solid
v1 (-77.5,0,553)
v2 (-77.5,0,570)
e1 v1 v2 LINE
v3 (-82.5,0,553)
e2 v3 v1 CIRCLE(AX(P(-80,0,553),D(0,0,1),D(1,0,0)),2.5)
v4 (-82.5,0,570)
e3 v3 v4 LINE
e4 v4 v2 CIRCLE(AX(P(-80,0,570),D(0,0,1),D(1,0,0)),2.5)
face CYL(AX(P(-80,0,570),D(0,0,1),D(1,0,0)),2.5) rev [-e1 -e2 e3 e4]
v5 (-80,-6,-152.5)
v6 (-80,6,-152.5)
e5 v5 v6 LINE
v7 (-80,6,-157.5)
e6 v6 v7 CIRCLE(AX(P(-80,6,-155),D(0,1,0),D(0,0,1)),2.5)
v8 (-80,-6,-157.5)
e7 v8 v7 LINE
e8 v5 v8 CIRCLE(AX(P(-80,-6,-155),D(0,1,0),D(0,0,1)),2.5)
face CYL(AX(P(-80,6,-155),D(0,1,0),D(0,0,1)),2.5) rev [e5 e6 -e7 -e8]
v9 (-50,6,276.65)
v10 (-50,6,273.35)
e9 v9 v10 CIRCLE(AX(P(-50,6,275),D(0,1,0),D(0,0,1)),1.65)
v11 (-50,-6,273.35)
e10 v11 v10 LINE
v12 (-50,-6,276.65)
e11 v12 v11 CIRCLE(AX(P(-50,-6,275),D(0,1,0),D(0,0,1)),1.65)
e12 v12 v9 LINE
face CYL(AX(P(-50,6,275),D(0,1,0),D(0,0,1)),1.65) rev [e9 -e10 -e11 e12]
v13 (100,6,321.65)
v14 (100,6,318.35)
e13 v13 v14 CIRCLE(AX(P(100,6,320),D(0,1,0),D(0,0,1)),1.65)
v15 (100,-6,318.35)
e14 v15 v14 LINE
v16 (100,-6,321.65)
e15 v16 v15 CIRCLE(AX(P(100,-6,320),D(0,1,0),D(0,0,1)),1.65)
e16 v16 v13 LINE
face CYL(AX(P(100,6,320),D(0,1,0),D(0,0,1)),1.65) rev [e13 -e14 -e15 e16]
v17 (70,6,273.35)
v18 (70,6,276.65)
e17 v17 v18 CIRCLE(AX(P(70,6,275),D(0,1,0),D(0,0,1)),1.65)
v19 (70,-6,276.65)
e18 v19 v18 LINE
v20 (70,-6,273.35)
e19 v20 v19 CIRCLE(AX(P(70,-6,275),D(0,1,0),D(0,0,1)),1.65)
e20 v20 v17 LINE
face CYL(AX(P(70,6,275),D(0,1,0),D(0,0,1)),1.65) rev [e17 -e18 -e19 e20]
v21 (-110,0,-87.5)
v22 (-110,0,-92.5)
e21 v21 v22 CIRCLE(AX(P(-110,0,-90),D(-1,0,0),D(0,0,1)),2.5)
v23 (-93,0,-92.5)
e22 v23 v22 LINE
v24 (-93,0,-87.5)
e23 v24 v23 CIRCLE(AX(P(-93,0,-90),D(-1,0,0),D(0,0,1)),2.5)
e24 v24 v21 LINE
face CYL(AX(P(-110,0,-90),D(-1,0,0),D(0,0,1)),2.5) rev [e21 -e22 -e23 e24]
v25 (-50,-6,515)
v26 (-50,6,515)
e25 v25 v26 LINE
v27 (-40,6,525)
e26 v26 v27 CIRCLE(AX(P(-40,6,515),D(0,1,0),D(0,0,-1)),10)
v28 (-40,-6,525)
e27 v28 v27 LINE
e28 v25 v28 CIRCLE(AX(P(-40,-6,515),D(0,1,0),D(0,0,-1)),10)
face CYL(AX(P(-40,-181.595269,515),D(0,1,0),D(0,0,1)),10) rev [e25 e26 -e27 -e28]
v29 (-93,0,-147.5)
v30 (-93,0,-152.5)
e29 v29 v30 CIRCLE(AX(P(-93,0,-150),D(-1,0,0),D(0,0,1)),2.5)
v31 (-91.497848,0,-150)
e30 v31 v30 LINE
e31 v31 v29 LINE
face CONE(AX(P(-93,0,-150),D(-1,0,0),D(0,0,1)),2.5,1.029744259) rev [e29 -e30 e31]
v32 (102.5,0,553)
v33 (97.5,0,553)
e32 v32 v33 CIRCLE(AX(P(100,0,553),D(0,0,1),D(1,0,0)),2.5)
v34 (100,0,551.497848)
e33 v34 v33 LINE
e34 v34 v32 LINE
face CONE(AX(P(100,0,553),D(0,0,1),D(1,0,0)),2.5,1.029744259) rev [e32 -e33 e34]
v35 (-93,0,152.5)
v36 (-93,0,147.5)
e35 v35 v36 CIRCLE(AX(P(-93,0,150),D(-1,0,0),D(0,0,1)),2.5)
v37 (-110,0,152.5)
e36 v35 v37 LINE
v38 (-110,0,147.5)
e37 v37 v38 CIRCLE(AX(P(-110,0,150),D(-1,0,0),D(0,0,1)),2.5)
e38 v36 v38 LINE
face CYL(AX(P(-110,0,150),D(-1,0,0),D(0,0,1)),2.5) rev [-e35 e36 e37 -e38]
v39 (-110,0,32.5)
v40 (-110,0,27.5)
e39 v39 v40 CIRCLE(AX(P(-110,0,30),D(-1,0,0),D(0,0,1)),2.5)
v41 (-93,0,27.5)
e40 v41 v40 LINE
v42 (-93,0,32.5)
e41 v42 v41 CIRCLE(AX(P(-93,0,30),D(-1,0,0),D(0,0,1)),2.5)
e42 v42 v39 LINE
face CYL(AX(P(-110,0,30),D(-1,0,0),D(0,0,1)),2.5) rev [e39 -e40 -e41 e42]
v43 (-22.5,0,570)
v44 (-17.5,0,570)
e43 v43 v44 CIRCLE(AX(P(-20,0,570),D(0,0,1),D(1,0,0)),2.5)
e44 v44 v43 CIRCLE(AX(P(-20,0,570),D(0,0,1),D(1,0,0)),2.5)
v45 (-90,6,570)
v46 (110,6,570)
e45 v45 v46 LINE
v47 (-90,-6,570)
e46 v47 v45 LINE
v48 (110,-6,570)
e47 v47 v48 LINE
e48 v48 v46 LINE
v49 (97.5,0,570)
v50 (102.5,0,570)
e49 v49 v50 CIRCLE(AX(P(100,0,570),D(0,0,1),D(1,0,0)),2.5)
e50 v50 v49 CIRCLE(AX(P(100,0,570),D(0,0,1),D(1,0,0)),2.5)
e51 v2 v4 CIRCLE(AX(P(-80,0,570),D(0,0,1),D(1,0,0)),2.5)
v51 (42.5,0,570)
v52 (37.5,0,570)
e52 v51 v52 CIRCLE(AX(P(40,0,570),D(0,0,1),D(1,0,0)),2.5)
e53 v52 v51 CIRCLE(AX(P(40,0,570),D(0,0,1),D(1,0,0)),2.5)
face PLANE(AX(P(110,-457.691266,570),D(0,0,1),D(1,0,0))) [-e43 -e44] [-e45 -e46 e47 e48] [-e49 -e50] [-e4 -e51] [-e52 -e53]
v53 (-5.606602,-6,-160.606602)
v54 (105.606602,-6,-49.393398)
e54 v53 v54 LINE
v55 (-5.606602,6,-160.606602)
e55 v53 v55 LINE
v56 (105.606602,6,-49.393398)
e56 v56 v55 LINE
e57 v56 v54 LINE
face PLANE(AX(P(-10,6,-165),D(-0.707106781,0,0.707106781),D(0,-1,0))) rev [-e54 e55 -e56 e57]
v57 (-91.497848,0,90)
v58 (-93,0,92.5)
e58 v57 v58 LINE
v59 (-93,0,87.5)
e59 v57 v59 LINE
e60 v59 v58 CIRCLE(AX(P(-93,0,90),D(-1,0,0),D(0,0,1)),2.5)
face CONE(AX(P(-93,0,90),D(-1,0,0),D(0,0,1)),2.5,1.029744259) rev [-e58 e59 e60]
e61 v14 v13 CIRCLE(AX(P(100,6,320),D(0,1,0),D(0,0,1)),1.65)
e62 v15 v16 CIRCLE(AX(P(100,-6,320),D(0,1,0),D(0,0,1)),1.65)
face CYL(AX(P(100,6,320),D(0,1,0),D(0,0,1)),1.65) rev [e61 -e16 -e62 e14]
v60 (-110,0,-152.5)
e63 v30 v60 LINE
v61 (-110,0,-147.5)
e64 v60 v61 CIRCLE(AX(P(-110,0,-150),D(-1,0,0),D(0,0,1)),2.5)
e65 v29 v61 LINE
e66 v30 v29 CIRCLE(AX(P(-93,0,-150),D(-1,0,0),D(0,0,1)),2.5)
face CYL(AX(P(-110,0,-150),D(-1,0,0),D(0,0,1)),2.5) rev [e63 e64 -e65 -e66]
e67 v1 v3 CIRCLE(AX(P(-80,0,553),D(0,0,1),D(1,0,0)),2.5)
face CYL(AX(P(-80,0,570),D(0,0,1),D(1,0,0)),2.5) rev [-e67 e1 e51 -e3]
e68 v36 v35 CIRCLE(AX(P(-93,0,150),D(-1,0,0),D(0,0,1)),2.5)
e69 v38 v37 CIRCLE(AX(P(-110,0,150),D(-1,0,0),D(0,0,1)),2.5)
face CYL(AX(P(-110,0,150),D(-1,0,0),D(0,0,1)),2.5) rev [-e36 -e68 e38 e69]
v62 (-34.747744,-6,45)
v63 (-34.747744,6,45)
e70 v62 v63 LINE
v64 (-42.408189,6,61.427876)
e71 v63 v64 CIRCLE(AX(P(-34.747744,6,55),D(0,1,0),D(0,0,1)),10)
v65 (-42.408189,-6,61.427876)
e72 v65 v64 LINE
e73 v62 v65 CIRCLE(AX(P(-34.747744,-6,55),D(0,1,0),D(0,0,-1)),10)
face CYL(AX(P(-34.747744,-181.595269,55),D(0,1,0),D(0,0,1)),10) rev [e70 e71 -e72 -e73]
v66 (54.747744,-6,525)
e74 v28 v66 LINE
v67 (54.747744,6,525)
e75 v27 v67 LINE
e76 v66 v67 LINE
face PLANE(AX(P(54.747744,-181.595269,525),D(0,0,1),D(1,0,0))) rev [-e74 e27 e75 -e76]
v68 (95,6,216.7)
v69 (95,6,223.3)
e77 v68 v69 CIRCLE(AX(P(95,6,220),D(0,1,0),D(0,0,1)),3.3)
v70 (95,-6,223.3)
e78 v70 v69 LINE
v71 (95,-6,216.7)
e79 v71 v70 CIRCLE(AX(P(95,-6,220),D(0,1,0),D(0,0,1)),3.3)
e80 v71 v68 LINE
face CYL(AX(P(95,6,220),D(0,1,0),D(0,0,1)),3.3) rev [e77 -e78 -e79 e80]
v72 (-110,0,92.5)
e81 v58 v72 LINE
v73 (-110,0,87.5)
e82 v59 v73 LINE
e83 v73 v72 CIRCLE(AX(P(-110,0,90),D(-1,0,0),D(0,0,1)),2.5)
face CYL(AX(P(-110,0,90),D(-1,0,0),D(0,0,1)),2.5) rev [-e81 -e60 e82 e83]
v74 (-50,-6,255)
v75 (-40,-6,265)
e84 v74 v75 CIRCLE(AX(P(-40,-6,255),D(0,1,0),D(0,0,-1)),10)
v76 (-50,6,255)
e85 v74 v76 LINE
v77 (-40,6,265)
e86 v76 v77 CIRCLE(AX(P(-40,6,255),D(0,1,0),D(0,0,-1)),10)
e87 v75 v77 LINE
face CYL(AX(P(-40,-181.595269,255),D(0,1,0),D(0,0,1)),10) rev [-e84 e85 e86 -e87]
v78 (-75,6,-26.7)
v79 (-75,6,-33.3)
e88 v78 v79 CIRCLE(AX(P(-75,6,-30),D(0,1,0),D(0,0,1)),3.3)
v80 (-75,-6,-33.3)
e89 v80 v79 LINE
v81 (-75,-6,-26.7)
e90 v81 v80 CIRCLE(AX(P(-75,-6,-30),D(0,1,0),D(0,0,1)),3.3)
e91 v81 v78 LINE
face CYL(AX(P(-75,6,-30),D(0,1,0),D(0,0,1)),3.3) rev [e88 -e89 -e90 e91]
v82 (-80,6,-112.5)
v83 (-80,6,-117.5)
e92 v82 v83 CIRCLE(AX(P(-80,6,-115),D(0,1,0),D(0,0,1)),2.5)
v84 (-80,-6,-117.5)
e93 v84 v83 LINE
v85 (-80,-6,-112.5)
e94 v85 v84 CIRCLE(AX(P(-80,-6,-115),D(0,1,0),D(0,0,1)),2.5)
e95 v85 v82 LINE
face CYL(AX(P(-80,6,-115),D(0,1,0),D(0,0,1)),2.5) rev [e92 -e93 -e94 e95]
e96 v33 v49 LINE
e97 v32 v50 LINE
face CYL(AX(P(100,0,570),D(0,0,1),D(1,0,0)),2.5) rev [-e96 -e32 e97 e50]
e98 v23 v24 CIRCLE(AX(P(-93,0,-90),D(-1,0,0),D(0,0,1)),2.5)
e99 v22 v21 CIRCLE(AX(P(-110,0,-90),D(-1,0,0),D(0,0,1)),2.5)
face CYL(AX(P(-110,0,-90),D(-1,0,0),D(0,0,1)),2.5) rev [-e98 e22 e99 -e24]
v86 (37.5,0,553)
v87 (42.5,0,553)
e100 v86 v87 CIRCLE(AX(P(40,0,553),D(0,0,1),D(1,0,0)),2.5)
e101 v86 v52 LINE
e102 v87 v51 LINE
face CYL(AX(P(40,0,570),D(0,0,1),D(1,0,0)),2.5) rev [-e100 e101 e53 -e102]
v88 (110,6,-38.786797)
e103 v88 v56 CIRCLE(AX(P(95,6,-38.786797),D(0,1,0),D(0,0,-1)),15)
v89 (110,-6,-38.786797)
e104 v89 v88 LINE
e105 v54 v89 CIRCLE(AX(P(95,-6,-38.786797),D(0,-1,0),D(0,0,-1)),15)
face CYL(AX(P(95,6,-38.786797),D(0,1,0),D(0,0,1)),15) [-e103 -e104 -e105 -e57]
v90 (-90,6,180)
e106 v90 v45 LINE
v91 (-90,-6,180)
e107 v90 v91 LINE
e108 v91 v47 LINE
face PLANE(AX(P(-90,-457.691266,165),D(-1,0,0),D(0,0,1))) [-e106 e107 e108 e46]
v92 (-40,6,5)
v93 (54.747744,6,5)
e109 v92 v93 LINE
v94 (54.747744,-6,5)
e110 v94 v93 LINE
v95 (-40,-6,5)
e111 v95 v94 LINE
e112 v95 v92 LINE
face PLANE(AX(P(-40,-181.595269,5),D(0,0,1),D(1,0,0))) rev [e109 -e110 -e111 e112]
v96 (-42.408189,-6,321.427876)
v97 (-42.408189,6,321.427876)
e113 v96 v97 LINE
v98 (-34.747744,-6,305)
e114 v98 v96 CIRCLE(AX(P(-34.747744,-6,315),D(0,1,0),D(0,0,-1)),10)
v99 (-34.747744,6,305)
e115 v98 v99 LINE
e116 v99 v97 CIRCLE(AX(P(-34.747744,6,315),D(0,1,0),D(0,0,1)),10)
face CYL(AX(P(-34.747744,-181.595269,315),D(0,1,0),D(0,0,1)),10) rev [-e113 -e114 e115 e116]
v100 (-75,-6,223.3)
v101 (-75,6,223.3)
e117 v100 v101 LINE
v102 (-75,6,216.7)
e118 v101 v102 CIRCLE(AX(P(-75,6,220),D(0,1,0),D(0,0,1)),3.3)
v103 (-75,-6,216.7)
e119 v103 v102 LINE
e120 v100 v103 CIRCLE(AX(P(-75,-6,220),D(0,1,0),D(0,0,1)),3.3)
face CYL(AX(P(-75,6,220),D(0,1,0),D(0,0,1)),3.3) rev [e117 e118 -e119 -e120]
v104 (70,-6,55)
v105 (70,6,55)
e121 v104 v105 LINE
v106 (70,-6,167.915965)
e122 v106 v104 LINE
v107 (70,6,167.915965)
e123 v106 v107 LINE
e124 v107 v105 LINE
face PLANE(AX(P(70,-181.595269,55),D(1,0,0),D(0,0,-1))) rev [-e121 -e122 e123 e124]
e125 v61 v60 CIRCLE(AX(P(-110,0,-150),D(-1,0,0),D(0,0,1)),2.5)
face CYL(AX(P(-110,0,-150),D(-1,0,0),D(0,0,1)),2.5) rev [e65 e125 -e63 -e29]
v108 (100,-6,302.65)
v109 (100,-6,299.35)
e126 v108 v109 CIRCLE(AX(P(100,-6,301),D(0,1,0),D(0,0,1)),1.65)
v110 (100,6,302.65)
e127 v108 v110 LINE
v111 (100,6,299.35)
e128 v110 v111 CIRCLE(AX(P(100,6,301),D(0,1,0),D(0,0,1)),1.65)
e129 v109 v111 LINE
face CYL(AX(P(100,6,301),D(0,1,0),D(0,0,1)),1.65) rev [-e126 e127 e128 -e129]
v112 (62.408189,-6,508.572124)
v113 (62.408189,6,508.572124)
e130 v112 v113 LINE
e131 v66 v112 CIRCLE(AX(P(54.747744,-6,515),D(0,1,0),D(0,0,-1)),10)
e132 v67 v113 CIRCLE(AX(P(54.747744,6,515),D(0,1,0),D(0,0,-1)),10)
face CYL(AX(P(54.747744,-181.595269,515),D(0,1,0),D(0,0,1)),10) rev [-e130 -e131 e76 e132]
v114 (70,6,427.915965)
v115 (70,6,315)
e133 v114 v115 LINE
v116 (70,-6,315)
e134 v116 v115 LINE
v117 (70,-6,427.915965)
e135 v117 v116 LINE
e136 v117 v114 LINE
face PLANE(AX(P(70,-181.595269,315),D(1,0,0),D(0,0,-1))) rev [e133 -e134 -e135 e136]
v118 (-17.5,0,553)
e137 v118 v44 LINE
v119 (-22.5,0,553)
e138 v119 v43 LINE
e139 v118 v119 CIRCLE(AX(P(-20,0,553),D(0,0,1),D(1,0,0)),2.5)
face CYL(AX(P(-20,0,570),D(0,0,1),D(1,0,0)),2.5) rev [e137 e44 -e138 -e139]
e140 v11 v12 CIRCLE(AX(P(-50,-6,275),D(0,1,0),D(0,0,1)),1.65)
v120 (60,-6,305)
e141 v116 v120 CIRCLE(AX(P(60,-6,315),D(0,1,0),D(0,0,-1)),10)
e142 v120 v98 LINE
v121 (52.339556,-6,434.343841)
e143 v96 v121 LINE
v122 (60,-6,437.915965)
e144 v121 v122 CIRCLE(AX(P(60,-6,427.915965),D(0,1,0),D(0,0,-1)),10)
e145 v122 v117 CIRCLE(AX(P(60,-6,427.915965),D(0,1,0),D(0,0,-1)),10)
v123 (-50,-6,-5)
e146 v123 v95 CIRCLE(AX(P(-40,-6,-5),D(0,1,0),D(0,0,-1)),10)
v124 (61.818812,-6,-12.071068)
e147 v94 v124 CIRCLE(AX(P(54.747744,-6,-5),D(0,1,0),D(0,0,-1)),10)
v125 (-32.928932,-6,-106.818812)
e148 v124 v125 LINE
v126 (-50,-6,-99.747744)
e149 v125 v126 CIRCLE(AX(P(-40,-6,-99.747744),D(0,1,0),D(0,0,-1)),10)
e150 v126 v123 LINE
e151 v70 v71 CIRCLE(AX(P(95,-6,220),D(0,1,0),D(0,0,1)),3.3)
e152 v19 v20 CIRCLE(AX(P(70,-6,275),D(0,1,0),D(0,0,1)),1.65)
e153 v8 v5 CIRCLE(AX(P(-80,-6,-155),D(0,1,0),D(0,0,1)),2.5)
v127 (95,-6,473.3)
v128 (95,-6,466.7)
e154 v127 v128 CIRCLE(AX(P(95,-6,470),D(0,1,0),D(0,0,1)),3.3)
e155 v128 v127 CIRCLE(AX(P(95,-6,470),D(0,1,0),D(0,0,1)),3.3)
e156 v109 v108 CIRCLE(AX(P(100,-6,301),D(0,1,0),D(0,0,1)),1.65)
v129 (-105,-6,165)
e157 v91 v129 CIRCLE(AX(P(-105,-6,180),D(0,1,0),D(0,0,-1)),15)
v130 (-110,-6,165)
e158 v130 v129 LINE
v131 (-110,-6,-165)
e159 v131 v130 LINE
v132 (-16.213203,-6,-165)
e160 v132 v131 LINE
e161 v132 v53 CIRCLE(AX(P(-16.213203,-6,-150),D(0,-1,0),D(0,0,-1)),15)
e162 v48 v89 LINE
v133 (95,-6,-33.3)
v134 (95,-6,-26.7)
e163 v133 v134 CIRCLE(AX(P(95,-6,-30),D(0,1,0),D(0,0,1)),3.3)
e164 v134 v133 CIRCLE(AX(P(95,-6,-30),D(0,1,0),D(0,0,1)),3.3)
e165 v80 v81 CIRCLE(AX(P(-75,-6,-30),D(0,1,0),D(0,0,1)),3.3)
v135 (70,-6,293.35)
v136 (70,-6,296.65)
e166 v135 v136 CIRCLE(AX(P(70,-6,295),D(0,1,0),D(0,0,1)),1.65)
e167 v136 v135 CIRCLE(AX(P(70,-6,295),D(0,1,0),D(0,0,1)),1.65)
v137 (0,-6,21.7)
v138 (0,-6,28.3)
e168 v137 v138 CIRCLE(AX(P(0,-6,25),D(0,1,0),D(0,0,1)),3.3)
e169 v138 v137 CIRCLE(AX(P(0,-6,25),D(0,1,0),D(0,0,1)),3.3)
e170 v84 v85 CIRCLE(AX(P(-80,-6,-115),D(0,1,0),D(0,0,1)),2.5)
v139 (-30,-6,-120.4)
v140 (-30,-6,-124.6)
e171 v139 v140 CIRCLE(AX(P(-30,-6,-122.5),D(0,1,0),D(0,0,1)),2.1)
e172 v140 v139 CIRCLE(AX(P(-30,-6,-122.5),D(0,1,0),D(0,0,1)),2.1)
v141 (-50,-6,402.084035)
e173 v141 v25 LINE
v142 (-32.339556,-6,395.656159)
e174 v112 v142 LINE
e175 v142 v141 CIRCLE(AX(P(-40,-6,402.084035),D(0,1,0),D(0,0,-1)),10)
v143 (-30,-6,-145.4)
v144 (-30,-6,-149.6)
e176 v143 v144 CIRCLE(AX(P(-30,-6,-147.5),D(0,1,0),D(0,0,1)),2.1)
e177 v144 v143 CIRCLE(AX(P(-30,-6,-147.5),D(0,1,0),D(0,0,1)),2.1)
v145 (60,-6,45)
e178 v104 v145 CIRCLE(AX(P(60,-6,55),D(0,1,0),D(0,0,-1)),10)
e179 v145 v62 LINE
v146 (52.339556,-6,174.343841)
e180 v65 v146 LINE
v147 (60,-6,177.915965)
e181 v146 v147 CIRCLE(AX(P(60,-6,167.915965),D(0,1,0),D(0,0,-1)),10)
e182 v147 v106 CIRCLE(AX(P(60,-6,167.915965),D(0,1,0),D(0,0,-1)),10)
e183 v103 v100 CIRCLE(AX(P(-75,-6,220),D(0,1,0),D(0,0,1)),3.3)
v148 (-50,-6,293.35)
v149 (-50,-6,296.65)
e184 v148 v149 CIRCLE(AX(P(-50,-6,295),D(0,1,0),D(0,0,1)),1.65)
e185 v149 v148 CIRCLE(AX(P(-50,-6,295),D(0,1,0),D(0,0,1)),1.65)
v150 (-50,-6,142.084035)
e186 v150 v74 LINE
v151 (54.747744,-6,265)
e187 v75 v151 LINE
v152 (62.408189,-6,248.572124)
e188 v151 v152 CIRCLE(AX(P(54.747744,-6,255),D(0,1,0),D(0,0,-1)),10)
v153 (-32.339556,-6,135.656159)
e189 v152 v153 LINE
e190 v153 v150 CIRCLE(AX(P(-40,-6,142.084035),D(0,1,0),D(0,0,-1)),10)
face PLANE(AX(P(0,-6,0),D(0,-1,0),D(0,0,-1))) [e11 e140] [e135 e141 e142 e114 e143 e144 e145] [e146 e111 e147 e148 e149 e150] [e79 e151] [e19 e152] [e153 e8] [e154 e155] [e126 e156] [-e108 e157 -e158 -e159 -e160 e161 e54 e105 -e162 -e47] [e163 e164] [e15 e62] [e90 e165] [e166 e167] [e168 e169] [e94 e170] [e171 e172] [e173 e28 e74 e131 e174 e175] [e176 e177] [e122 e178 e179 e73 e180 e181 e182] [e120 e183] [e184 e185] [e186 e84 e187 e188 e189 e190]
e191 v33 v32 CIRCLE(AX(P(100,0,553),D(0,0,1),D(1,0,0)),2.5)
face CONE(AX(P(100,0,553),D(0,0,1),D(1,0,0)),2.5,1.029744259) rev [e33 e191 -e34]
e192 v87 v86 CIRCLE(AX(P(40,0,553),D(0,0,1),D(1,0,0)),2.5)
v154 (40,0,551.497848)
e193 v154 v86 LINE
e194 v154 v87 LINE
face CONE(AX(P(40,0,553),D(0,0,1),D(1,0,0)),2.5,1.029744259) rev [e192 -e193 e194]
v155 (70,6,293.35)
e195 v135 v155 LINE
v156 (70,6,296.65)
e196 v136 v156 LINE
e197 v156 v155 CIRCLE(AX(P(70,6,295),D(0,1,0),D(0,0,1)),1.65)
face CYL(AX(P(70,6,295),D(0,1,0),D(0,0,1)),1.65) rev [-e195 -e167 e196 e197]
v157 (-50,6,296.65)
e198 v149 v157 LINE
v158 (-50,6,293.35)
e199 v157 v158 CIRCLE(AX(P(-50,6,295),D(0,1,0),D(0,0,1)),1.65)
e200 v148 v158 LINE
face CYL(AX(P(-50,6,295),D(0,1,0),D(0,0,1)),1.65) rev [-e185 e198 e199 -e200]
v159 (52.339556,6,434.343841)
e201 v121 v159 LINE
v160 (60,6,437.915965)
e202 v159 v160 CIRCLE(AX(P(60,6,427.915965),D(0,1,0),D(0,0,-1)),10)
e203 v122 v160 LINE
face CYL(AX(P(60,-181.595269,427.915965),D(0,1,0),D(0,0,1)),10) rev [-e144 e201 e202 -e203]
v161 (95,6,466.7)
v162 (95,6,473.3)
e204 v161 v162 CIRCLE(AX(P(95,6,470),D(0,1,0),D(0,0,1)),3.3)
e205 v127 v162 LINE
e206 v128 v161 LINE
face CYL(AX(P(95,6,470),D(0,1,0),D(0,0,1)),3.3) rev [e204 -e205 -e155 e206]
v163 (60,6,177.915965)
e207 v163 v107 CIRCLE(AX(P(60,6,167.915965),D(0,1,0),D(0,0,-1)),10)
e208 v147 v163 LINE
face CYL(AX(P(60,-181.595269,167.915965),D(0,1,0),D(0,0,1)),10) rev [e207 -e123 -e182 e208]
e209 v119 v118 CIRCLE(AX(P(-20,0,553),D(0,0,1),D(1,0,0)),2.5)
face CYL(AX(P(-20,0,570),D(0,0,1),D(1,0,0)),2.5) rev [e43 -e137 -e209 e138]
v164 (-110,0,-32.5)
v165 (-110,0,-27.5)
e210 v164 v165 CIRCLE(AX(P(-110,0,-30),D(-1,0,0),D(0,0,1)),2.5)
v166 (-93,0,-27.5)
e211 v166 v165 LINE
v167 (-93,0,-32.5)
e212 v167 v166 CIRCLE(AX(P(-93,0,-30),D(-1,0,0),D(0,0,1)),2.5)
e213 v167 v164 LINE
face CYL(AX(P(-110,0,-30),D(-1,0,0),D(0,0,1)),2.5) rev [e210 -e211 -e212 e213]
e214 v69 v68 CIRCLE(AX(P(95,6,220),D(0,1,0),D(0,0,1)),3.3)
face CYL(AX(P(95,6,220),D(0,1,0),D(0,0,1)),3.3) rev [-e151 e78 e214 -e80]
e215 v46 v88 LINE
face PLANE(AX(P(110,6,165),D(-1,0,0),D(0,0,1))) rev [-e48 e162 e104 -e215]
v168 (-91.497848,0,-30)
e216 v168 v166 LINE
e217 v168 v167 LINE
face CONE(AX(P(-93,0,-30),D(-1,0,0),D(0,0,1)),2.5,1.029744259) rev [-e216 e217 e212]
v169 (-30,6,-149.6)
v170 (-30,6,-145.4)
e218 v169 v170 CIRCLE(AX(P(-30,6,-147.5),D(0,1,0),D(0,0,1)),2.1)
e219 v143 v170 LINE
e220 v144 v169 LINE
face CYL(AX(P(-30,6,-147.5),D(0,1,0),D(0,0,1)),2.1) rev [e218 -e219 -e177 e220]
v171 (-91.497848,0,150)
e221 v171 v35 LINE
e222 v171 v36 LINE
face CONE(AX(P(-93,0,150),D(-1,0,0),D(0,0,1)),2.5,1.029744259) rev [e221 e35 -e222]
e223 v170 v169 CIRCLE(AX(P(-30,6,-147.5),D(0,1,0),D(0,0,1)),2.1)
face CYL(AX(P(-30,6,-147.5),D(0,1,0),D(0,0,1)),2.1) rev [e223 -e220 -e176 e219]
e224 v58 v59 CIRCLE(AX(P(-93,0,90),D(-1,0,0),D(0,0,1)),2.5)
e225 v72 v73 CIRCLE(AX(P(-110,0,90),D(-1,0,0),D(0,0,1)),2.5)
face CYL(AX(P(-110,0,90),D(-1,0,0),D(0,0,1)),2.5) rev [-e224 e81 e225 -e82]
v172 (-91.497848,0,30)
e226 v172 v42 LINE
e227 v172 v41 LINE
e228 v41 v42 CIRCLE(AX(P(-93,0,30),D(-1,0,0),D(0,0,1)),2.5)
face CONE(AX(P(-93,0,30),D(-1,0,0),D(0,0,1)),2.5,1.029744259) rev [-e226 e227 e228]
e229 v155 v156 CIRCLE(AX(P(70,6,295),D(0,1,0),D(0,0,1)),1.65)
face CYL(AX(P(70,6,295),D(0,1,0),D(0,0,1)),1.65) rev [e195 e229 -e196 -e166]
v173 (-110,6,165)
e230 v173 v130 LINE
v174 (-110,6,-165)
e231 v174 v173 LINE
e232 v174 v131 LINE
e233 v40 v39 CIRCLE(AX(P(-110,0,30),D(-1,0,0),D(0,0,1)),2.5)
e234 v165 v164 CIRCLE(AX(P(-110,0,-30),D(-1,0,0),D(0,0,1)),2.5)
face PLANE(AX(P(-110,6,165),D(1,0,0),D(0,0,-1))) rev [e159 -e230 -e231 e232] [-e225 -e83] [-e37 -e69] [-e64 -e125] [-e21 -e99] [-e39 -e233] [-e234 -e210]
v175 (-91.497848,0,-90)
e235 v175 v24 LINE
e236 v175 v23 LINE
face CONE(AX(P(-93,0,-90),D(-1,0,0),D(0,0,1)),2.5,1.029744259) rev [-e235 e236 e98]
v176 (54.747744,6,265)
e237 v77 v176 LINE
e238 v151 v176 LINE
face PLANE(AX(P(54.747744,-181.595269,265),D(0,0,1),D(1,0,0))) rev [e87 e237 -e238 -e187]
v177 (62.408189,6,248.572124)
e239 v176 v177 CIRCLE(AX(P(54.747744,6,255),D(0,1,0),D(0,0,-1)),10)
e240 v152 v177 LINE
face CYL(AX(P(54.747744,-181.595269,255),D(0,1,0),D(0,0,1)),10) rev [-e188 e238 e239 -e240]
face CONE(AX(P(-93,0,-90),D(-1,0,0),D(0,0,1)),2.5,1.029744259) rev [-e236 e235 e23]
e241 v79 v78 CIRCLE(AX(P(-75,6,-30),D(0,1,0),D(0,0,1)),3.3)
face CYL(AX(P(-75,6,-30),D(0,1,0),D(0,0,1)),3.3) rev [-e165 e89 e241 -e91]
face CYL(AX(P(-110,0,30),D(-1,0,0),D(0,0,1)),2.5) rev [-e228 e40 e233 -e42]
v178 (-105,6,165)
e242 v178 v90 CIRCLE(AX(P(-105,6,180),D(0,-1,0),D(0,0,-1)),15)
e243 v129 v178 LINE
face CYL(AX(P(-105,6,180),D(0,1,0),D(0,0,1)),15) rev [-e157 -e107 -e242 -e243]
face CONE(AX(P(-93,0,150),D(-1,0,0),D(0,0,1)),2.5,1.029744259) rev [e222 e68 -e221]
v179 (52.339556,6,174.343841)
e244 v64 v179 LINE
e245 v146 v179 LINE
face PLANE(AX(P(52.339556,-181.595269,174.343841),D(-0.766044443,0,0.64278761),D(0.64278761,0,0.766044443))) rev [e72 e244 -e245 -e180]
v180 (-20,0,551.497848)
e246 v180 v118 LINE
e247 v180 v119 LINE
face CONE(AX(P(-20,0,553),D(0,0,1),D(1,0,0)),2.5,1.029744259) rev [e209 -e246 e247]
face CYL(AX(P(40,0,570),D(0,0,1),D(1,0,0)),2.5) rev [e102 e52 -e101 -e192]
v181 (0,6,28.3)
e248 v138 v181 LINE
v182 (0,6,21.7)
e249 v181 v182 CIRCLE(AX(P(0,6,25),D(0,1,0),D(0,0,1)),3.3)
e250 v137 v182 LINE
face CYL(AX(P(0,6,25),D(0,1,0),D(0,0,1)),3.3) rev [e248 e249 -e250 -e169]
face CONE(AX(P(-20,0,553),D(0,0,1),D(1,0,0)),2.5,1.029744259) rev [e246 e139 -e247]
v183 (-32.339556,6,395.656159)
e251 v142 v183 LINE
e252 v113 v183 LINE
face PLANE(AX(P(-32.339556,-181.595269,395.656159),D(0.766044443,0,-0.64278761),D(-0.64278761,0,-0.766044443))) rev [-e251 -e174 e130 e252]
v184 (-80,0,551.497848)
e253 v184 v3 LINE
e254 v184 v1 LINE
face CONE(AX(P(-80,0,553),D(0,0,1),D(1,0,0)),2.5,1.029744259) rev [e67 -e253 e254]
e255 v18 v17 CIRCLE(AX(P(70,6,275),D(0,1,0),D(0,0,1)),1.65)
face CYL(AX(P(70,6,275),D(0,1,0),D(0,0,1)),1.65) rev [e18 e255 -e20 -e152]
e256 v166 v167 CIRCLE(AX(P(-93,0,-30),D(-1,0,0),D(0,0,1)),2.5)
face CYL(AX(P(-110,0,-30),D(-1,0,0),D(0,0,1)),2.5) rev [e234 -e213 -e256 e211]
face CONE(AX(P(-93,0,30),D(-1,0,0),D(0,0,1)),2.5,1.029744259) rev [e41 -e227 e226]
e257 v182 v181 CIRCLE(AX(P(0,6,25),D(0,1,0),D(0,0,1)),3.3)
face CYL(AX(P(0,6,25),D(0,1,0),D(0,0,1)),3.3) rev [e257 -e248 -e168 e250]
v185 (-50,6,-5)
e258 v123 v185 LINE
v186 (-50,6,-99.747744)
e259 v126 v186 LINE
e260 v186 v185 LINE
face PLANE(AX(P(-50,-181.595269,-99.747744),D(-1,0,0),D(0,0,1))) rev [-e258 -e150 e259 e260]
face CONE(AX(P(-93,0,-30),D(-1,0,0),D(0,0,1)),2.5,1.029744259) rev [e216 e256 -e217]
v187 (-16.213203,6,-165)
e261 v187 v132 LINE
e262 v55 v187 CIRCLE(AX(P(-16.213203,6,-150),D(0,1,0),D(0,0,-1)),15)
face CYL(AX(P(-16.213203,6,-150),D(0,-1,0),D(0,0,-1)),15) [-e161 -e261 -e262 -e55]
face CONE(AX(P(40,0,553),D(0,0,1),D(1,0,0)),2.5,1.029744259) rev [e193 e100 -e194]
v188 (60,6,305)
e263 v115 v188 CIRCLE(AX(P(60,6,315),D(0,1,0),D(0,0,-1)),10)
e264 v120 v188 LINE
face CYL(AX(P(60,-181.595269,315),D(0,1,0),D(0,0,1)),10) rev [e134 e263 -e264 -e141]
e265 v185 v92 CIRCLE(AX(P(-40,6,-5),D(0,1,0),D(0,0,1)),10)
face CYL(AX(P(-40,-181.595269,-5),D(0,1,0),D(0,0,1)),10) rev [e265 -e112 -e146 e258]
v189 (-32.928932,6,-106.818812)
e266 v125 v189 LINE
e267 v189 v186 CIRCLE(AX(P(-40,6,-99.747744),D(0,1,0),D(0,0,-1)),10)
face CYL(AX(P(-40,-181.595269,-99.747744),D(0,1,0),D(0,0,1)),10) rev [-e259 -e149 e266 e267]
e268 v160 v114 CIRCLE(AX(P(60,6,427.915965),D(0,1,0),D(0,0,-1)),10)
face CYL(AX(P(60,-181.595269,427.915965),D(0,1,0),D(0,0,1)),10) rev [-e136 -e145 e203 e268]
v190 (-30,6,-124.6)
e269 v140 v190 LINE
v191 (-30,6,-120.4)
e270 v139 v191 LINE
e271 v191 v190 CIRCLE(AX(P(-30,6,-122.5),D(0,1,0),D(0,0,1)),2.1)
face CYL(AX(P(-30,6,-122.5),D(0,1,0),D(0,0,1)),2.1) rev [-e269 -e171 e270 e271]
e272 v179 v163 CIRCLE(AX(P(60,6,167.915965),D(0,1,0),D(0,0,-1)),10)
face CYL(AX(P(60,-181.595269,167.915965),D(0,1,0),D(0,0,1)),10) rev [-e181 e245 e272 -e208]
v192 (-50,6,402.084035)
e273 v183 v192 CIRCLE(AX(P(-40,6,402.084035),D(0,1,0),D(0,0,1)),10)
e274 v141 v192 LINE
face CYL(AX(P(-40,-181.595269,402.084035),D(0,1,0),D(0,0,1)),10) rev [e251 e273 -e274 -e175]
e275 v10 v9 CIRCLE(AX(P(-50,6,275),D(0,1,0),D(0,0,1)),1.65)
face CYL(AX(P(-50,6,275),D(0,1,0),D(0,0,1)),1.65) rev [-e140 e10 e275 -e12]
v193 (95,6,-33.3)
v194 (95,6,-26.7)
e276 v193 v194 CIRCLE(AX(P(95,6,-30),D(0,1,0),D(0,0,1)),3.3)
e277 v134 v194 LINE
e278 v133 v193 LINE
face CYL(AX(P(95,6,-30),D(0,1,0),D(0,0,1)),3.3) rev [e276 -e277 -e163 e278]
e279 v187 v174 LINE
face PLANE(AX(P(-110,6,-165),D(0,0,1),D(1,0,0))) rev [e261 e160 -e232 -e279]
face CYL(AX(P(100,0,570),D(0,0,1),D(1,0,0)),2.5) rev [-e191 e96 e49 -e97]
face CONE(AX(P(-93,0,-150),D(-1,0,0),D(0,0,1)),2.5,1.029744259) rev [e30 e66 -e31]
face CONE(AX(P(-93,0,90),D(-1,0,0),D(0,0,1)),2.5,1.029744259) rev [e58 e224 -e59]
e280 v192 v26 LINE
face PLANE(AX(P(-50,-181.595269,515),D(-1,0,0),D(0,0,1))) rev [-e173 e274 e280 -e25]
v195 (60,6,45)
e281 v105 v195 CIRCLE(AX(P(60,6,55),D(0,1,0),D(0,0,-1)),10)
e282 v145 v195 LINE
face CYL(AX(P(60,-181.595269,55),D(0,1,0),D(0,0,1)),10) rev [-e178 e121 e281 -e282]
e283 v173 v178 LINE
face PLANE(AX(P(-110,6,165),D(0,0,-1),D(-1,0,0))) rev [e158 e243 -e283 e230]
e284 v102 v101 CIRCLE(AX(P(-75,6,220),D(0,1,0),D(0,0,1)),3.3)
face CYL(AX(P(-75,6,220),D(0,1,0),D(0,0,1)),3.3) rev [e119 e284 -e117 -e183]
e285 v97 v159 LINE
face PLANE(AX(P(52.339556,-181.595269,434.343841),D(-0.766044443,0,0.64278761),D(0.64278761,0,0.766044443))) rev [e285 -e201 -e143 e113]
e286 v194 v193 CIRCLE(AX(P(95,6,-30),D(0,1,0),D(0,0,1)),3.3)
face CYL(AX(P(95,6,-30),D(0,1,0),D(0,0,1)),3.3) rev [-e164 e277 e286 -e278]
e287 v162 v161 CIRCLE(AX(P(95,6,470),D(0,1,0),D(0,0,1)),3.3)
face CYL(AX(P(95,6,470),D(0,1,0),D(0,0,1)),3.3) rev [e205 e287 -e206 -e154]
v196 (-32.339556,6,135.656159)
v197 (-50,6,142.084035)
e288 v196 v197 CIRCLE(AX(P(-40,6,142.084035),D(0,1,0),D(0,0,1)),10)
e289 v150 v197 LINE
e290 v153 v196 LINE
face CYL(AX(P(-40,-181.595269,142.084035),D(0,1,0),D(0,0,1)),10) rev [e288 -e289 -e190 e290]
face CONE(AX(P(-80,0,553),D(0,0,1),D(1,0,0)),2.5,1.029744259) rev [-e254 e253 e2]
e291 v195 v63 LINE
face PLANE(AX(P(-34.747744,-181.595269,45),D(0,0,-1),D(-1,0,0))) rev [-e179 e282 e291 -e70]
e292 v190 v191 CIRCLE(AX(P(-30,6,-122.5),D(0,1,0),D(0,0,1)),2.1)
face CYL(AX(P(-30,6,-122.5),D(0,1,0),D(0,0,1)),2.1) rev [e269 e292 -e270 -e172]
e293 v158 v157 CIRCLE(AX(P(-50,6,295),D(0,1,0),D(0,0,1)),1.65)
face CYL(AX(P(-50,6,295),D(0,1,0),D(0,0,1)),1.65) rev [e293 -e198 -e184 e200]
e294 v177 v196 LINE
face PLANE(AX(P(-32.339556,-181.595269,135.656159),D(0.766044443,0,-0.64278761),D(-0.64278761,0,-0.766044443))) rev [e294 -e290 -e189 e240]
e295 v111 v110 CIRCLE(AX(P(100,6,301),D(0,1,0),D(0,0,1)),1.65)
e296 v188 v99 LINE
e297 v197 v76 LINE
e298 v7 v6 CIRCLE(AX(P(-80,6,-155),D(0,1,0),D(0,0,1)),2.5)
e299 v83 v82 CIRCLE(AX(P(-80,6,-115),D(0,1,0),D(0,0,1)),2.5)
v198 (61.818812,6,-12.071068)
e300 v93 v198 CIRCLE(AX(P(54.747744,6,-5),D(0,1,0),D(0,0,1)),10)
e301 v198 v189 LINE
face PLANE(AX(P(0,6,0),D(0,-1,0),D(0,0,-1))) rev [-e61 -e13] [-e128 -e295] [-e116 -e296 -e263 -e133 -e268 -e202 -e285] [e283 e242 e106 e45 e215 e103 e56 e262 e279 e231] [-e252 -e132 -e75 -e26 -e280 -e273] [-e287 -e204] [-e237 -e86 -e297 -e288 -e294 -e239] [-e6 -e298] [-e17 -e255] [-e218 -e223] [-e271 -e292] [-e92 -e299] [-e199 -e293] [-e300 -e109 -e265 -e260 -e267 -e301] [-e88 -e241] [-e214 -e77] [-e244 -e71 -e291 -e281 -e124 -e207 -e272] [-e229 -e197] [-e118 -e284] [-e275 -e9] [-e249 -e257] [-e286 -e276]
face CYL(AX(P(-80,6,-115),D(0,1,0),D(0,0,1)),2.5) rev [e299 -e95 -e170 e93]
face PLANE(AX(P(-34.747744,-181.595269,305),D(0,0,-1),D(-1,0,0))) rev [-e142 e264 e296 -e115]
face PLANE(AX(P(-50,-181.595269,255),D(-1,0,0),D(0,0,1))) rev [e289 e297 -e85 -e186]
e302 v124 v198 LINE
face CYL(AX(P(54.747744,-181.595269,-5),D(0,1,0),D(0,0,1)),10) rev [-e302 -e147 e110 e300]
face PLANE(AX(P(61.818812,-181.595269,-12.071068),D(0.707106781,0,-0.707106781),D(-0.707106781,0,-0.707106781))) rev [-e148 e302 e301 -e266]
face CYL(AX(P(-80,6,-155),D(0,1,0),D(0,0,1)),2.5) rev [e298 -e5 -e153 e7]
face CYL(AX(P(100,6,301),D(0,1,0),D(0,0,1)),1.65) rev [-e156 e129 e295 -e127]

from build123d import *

# Parameters (mm, degrees)
SKETCH_1_W             = 220
SKETCH_1_H             = 330
EXTRUDE_1_DEPTH        = 6
SKETCH_2_W             = 200
SKETCH_2_H             = 405
EXTRUDE_2_DEPTH        = 12
CHAMFER_1_SIZE         = 120
FILLET_2_R             = 15
CUT_EXTRUDE_3_DEPTH    = 12
HOLE_WIZARD_M6_1_D     = 5
HOLE_WIZARD_M6_1_DEPTH = 17
HOLE_WIZARD_M6_1_TIP   = 1.502151548
HOLE_WIZARD_M6_2_D     = 5
HOLE_WIZARD_M6_2_DEPTH = 17
HOLE_WIZARD_M6_2_TIP   = 1.502151548
HOLE_WIZARD_M6_1_2_D   = 6.6
HOLE_WIZARD_M6_2_2_D   = 6.6
HOLE_WIZARD_M6_3_D     = 5
HOLE_WIZARD_M5_1_D     = 4.2
HOLE_WIZARD_M4_1_D     = 3.3
HOLE_WIZARD_M4_2_D     = 3.3


with BuildPart() as part:
    # 草图1 → 凸台-拉伸1 (new, symmetric)
    with BuildSketch(Plane(origin=(0, 0, 0), x_dir=(1, 0, 0), z_dir=(0, 1, 0))):
        Rectangle(SKETCH_1_W, SKETCH_1_H)
    extrude(amount=EXTRUDE_1_DEPTH, both=True)

    # 草图2 → 凸台-拉伸2 (add)
    with BuildSketch(Plane(origin=(0, 6, 0), x_dir=(1, 0, 0), z_dir=(0, 1, 0))):
        with Locations((10, -367.5)):
            Rectangle(SKETCH_2_W, SKETCH_2_H)
    extrude(amount=-EXTRUDE_2_DEPTH)

    # 倒角1
    chamfer_1_edges = [part.edges().sort_by_distance(p)[0] for p in [
        (110, 0, -165),
    ]]
    chamfer(chamfer_1_edges, length=CHAMFER_1_SIZE)

    # 圆角2
    fillet_2_edges = [part.edges().sort_by_distance(p)[0] for p in [
        (-10, 0, -165),
        (110, 0, -45),
        (-90, 0, 165),
    ]]
    fillet(fillet_2_edges, radius=FILLET_2_R)

    # 草图7 → 切除-拉伸3 (cut)
    with BuildSketch(Plane(origin=(0, 6, 0), x_dir=(1, 0, 0), z_dir=(0, 1, 0))):
        with BuildLine():
            Line((-34.747744438, -45), (60, -45))
            ThreePointArc((60, -45), (67.071067812, -47.928932188), (70, -55))
            Line((70, -55), (70, -167.915964824))
            ThreePointArc((70, -167.915964824), (63.420201433, -177.312891032), (52.339555569, -174.343840921))
            Line((52.339555569, -174.343840921), (-42.408188869, -61.427876097))
            ThreePointArc((-42.408188869, -61.427876097), (-43.810822308, -50.773817383), (-34.747744438, -45))
        make_face()
        with BuildLine():
            Line((-32.339555569, -135.656159079), (62.408188869, -248.572123903))
            ThreePointArc((62.408188869, -248.572123903), (63.810822308, -259.226182617), (54.747744438, -265))
            Line((54.747744438, -265), (-40, -265))
            ThreePointArc((-40, -265), (-47.071067812, -262.071067812), (-50, -255))
            Line((-50, -255), (-50, -142.084035176))
            ThreePointArc((-50, -142.084035176), (-43.420201433, -132.687108968), (-32.339555569, -135.656159079))
        make_face()
        with BuildLine():
            Line((-34.747744438, -305), (60, -305))
            ThreePointArc((60, -305), (67.071067812, -307.928932188), (70, -315))
            Line((70, -315), (70, -427.915964824))
            ThreePointArc((70, -427.915964824), (63.420201433, -437.312891032), (52.339555569, -434.343840921))
            Line((52.339555569, -434.343840921), (-42.408188869, -321.427876097))
            ThreePointArc((-42.408188869, -321.427876097), (-43.810822308, -310.773817383), (-34.747744438, -305))
        make_face()
        with BuildLine():
            Line((-32.339555569, -395.656159079), (62.408188869, -508.572123903))
            ThreePointArc((62.408188869, -508.572123903), (63.810822308, -519.226182617), (54.747744438, -525))
            Line((54.747744438, -525), (-40, -525))
            ThreePointArc((-40, -525), (-47.071067812, -522.071067812), (-50, -515))
            Line((-50, -515), (-50, -402.084035176))
            ThreePointArc((-50, -402.084035176), (-43.420201433, -392.687108968), (-32.339555569, -395.656159079))
        make_face()
        with BuildLine():
            Line((-50, 99.747744438), (-50, 5))
            ThreePointArc((-50, 5), (-47.071067812, -2.071067812), (-40, -5))
            Line((-40, -5), (54.747744438, -5))
            ThreePointArc((54.747744438, -5), (63.986539763, 1.173165676), (61.81881225, 12.071067812))
            Line((61.81881225, 12.071067812), (-32.928932188, 106.81881225))
            ThreePointArc((-32.928932188, 106.81881225), (-43.826834324, 108.986539763), (-50, 99.747744438))
        make_face()
    extrude(amount=-CUT_EXTRUDE_3_DEPTH, mode=Mode.SUBTRACT)

    # Hole Wizard M6 _1
    with Locations(Plane.XY.offset(570)):
        with Locations((-80, 0), (-20, 0), (40, 0), (100, 0)):
            Hole(HOLE_WIZARD_M6_1_D / 2, depth=HOLE_WIZARD_M6_1_DEPTH)
            with Locations((0, 0, -(HOLE_WIZARD_M6_1_DEPTH + HOLE_WIZARD_M6_1_TIP / 2))):  # 118° drill point
                Cone(0, HOLE_WIZARD_M6_1_D / 2, HOLE_WIZARD_M6_1_TIP, mode=Mode.SUBTRACT)

    # Hole Wizard M6 _2
    with Locations(Plane.ZY.offset(110)):
        with Locations((-150, 0), (-90, 0), (-30, 0), (30, 0), (90, 0), (150, 0)):
            Hole(HOLE_WIZARD_M6_2_D / 2, depth=HOLE_WIZARD_M6_2_DEPTH)
            with Locations((0, 0, -(HOLE_WIZARD_M6_2_DEPTH + HOLE_WIZARD_M6_2_TIP / 2))):  # 118° drill point
                Cone(0, HOLE_WIZARD_M6_2_D / 2, HOLE_WIZARD_M6_2_TIP, mode=Mode.SUBTRACT)

    # Hole Wizard M6 _1 2 (through all)
    with Locations(Plane(origin=(0, 6, 0), x_dir=(1, 0, 0), z_dir=(0, 1, 0))):
        with Locations((95, 30), (-75, 30), (-75, -220), (95, -220), (95, -470)):
            Hole(HOLE_WIZARD_M6_1_2_D / 2)

    # Hole Wizard M6 _2 2 (through all)
    with Locations(Plane(origin=(0, 6, 0), x_dir=(1, 0, 0), z_dir=(0, 1, 0))):
        with Locations((0, -25)):
            Hole(HOLE_WIZARD_M6_2_2_D / 2)

    # M6 螺纹孔3 (through all)
    with Locations(Plane(origin=(0, 6, 0), x_dir=(1, 0, 0), z_dir=(0, 1, 0))):
        with Locations((-80, 155), (-80, 115)):
            Hole(HOLE_WIZARD_M6_3_D / 2)

    # M5 螺纹孔1 (through all)
    with Locations(Plane(origin=(0, 6, 0), x_dir=(1, 0, 0), z_dir=(0, 1, 0))):
        with Locations((-30, 147.5), (-30, 122.5)):
            Hole(HOLE_WIZARD_M5_1_D / 2)

    # M4 螺纹孔1 (through all)
    with Locations(Plane(origin=(0, 6, 0), x_dir=(1, 0, 0), z_dir=(0, 1, 0))):
        with Locations((100, -320), (100, -301)):
            Hole(HOLE_WIZARD_M4_1_D / 2)

    # M4 螺纹孔2 (through all)
    with Locations(Plane(origin=(0, 6, 0), x_dir=(1, 0, 0), z_dir=(0, 1, 0))):
        with Locations((-50, -275), (70, -275), (70, -295), (-50, -295)):
            Hole(HOLE_WIZARD_M4_2_D / 2)


solid = part.part
